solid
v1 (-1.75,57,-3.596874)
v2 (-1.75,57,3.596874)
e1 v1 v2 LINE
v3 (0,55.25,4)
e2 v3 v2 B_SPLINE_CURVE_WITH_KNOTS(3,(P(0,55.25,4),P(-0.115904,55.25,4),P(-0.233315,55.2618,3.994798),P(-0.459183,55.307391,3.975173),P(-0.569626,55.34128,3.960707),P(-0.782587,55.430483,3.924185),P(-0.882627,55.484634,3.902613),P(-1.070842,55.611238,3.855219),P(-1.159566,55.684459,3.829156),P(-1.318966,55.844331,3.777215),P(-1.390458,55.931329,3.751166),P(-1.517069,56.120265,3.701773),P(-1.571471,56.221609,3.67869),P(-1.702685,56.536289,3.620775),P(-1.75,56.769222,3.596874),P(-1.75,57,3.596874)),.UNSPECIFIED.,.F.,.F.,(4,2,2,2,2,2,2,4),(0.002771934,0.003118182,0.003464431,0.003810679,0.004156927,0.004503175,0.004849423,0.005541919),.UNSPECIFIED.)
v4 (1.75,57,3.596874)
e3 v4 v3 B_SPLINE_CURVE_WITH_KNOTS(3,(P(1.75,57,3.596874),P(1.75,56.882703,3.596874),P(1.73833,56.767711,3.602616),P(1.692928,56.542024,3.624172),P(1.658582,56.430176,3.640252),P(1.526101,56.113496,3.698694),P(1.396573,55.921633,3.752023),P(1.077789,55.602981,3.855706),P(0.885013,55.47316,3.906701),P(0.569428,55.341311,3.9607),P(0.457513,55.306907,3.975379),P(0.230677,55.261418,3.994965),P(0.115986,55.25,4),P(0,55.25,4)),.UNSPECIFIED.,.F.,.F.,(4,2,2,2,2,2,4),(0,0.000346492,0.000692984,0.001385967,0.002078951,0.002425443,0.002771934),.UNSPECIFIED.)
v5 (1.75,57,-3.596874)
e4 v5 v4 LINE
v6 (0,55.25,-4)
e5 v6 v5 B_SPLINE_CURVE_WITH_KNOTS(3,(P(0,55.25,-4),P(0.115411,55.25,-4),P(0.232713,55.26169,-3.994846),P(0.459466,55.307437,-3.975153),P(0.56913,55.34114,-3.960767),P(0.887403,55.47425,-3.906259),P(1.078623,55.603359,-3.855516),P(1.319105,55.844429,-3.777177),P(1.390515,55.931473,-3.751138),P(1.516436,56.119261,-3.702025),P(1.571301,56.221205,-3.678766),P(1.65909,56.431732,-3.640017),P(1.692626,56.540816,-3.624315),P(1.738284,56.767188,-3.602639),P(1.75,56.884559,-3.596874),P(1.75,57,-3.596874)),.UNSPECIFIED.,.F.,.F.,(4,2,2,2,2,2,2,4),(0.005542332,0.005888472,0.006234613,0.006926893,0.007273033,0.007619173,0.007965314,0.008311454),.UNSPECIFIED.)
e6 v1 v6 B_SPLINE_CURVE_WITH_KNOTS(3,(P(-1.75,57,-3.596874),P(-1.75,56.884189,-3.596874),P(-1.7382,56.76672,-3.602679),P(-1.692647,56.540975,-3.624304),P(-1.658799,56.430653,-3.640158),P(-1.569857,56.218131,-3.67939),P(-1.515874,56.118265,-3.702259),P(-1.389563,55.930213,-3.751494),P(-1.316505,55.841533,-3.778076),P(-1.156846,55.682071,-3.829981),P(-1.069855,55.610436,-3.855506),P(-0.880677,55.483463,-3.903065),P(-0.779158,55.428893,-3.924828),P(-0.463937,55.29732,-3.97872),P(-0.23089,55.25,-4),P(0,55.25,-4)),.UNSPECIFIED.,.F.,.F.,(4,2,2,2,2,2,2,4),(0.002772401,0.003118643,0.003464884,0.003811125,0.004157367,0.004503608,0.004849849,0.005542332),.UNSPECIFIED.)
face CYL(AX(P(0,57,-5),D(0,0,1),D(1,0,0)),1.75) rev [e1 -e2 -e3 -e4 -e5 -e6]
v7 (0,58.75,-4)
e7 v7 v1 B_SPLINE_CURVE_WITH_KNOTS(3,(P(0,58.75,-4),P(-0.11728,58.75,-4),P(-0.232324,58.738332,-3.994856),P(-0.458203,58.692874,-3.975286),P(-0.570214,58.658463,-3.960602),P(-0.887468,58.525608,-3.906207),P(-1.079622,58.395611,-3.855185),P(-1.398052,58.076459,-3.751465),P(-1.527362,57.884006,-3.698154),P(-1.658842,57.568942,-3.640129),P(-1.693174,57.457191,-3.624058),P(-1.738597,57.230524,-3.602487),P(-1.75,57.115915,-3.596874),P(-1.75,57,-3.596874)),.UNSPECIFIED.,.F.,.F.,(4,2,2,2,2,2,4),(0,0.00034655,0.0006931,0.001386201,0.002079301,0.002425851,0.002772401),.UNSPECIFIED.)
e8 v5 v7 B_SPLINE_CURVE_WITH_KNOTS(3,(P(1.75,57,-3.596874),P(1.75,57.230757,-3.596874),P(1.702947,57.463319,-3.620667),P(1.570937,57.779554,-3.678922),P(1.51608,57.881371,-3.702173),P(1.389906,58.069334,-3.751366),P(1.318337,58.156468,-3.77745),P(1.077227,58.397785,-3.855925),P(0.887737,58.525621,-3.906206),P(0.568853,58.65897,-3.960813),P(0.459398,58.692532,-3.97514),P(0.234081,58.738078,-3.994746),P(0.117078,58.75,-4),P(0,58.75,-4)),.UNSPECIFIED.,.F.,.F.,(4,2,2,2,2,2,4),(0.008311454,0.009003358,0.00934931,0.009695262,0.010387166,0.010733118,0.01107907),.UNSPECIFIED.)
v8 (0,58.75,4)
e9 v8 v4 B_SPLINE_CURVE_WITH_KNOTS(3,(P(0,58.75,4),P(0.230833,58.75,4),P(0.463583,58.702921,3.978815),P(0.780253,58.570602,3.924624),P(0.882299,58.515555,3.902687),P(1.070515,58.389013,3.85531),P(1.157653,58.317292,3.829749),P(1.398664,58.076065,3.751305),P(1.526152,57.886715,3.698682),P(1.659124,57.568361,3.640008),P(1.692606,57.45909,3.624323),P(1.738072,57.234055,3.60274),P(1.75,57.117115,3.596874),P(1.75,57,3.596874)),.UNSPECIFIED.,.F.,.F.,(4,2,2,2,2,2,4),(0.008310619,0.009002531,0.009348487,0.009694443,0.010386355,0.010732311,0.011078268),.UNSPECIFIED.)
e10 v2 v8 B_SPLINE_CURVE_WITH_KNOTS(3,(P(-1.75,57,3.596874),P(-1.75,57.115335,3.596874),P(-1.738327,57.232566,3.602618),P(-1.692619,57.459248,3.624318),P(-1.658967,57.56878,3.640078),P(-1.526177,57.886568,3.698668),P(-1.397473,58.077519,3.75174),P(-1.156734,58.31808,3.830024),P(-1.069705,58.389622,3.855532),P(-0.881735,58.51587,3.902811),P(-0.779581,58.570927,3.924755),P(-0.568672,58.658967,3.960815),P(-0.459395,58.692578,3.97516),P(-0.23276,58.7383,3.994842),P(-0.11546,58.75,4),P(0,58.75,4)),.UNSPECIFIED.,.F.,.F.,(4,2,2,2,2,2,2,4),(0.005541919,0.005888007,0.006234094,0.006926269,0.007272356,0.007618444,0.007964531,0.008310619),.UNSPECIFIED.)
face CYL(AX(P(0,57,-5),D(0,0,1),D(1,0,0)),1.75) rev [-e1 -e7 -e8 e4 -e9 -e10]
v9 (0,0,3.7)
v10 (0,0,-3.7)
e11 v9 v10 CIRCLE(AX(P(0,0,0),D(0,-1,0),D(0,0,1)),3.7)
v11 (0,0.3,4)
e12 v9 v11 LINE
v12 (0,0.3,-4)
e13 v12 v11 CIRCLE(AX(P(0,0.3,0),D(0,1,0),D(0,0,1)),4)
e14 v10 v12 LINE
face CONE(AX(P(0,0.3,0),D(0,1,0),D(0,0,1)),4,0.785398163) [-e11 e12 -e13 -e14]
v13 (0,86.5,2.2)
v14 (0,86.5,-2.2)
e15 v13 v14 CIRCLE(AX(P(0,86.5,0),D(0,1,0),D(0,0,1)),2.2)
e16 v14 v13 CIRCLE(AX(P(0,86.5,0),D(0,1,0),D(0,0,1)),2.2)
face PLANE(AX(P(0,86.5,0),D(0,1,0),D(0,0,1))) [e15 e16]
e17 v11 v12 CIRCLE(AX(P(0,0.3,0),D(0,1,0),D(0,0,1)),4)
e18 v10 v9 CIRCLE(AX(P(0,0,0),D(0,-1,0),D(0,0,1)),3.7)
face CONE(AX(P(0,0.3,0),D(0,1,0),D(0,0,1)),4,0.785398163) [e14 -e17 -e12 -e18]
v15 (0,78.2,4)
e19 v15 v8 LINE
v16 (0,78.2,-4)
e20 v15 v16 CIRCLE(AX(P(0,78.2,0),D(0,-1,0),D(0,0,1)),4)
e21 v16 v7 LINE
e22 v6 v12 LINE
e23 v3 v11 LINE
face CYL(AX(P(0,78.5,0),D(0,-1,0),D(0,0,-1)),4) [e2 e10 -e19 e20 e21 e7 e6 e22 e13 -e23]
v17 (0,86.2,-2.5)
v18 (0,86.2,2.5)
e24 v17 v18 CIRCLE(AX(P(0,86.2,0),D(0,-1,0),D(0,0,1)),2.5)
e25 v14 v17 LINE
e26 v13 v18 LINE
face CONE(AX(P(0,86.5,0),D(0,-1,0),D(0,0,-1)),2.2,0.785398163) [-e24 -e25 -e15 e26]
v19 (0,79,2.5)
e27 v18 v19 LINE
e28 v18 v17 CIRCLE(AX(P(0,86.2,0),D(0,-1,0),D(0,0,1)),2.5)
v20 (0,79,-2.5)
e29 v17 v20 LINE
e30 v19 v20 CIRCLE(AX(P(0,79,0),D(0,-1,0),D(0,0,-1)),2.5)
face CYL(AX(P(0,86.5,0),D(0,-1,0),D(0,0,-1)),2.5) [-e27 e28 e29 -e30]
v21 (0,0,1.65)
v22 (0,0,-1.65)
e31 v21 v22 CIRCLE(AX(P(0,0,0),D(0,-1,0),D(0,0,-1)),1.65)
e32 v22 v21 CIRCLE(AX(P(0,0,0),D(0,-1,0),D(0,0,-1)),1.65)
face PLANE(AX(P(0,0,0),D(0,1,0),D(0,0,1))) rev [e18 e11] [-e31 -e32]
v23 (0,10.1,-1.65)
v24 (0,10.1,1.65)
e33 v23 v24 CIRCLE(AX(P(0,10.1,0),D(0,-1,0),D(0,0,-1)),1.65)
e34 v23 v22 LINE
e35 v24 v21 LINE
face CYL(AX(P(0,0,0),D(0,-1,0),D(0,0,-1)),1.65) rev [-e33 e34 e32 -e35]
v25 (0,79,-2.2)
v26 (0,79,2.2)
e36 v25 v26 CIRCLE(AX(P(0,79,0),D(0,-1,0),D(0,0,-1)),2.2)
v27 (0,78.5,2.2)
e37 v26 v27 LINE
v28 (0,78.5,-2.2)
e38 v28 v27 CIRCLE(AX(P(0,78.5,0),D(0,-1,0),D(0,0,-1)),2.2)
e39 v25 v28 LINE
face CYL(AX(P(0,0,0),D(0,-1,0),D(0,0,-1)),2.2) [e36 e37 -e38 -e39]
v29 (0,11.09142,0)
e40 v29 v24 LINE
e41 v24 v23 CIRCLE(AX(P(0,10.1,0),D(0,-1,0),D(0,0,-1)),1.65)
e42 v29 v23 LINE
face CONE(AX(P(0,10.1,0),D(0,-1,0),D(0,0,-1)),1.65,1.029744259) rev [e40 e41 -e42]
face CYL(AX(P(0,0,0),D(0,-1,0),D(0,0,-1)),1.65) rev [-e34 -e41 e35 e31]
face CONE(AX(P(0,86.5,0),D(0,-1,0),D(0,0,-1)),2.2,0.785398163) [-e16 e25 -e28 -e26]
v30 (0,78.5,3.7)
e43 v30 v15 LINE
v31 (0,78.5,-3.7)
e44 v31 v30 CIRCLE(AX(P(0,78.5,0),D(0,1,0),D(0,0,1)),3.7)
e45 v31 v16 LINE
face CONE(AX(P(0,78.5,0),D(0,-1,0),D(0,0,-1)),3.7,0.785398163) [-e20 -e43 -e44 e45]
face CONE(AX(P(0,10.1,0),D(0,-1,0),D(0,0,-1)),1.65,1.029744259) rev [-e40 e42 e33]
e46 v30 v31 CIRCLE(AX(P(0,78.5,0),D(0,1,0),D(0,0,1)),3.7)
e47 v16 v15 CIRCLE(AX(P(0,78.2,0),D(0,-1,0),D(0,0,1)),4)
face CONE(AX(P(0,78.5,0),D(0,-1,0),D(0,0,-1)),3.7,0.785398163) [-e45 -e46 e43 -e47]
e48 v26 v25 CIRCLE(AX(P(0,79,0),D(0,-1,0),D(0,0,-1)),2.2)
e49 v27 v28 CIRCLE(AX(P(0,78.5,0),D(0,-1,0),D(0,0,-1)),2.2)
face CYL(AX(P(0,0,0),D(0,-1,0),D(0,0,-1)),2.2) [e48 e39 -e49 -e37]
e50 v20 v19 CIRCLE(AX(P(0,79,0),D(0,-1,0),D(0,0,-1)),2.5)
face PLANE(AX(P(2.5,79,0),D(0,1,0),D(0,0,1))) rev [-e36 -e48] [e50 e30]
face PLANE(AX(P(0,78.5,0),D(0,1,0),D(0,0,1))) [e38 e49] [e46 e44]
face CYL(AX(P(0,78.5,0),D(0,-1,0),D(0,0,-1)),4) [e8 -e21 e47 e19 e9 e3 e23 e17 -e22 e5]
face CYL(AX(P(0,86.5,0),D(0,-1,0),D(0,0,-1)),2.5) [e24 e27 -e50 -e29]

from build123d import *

# Parameters (mm, degrees)
SKETCH1_R             = 4
BOSS_EXTRUDE1_DEPTH   = 78.5
SKETCH2_R             = 2.5
BOSS_EXTRUDE2_DEPTH   = 8
CHAMFER1_SIZE         = 0.3
M4_TAPPED_HOLE1_D     = 3.3
M4_TAPPED_HOLE1_DEPTH = 10.1
M4_TAPPED_HOLE1_TIP   = 0.991420021
SKETCH6_R             = 1.75
CUT_EXTRUDE1_DEPTH    = 5
SKETCH7_W             = 0.3
SKETCH7_H             = 0.5


with BuildPart() as part:
    # Sketch1 → Boss-Extrude1 (new body)
    with BuildSketch(Plane(origin=(0, 0, 0), x_dir=(1, 0, 0), z_dir=(0, 1, 0))):
        with Locations(Location((0, 0, 0), (0, 0, 270))):
            Circle(SKETCH1_R)
    extrude(amount=BOSS_EXTRUDE1_DEPTH)

    # Sketch2 → Boss-Extrude2 (add)
    with BuildSketch(Plane(origin=(0, 78.5, 0), x_dir=(1, 0, 0), z_dir=(0, 1, 0))):
        with Locations(Location((0, 0, 0), (0, 0, 270))):
            Circle(SKETCH2_R)
    extrude(amount=BOSS_EXTRUDE2_DEPTH)

    # Chamfer1
    chamfer1_edges = [part.edges().sort_by_distance(p)[0] for p in [
        (0, 0, -4),
        (0, 78.5, -4),
        (0, 86.5, -2.5),
    ]]
    chamfer(chamfer1_edges, length=CHAMFER1_SIZE)

    # M4 Tapped Hole1
    with Locations(Plane(origin=(0, 0, 0), x_dir=(-1, 0, 0), z_dir=(0, -1, 0))):
        with Locations((0, 0)):
            Hole(M4_TAPPED_HOLE1_D / 2, depth=M4_TAPPED_HOLE1_DEPTH)
            with Locations((0, 0, -(M4_TAPPED_HOLE1_DEPTH + M4_TAPPED_HOLE1_TIP / 2))):  # 118° drill point
                Cone(0, M4_TAPPED_HOLE1_D / 2, M4_TAPPED_HOLE1_TIP, mode=Mode.SUBTRACT)

    # Sketch6 → Cut-Extrude1 (cut, symmetric)
    with BuildSketch(Plane.XY):
        with Locations(Location((0, 57, 0), (0, 0, 90))):
            Circle(SKETCH6_R)
    extrude(amount=CUT_EXTRUDE1_DEPTH, both=True, mode=Mode.SUBTRACT)

    # Sketch7 → Cut-Revolve1 (revolve, cut)
    with BuildSketch(Plane.XY, mode=Mode.PRIVATE) as cut_revolve1_sk:
        with Locations((2.35, 78.75)):
            Rectangle(SKETCH7_W, SKETCH7_H)
    revolve(cut_revolve1_sk.sketch.rotate(Axis((0, 0, 0), (0, 1, 0)), 90), axis=Axis((0, 0, 0), (0, 1, 0)), mode=Mode.SUBTRACT)


solid = part.part
